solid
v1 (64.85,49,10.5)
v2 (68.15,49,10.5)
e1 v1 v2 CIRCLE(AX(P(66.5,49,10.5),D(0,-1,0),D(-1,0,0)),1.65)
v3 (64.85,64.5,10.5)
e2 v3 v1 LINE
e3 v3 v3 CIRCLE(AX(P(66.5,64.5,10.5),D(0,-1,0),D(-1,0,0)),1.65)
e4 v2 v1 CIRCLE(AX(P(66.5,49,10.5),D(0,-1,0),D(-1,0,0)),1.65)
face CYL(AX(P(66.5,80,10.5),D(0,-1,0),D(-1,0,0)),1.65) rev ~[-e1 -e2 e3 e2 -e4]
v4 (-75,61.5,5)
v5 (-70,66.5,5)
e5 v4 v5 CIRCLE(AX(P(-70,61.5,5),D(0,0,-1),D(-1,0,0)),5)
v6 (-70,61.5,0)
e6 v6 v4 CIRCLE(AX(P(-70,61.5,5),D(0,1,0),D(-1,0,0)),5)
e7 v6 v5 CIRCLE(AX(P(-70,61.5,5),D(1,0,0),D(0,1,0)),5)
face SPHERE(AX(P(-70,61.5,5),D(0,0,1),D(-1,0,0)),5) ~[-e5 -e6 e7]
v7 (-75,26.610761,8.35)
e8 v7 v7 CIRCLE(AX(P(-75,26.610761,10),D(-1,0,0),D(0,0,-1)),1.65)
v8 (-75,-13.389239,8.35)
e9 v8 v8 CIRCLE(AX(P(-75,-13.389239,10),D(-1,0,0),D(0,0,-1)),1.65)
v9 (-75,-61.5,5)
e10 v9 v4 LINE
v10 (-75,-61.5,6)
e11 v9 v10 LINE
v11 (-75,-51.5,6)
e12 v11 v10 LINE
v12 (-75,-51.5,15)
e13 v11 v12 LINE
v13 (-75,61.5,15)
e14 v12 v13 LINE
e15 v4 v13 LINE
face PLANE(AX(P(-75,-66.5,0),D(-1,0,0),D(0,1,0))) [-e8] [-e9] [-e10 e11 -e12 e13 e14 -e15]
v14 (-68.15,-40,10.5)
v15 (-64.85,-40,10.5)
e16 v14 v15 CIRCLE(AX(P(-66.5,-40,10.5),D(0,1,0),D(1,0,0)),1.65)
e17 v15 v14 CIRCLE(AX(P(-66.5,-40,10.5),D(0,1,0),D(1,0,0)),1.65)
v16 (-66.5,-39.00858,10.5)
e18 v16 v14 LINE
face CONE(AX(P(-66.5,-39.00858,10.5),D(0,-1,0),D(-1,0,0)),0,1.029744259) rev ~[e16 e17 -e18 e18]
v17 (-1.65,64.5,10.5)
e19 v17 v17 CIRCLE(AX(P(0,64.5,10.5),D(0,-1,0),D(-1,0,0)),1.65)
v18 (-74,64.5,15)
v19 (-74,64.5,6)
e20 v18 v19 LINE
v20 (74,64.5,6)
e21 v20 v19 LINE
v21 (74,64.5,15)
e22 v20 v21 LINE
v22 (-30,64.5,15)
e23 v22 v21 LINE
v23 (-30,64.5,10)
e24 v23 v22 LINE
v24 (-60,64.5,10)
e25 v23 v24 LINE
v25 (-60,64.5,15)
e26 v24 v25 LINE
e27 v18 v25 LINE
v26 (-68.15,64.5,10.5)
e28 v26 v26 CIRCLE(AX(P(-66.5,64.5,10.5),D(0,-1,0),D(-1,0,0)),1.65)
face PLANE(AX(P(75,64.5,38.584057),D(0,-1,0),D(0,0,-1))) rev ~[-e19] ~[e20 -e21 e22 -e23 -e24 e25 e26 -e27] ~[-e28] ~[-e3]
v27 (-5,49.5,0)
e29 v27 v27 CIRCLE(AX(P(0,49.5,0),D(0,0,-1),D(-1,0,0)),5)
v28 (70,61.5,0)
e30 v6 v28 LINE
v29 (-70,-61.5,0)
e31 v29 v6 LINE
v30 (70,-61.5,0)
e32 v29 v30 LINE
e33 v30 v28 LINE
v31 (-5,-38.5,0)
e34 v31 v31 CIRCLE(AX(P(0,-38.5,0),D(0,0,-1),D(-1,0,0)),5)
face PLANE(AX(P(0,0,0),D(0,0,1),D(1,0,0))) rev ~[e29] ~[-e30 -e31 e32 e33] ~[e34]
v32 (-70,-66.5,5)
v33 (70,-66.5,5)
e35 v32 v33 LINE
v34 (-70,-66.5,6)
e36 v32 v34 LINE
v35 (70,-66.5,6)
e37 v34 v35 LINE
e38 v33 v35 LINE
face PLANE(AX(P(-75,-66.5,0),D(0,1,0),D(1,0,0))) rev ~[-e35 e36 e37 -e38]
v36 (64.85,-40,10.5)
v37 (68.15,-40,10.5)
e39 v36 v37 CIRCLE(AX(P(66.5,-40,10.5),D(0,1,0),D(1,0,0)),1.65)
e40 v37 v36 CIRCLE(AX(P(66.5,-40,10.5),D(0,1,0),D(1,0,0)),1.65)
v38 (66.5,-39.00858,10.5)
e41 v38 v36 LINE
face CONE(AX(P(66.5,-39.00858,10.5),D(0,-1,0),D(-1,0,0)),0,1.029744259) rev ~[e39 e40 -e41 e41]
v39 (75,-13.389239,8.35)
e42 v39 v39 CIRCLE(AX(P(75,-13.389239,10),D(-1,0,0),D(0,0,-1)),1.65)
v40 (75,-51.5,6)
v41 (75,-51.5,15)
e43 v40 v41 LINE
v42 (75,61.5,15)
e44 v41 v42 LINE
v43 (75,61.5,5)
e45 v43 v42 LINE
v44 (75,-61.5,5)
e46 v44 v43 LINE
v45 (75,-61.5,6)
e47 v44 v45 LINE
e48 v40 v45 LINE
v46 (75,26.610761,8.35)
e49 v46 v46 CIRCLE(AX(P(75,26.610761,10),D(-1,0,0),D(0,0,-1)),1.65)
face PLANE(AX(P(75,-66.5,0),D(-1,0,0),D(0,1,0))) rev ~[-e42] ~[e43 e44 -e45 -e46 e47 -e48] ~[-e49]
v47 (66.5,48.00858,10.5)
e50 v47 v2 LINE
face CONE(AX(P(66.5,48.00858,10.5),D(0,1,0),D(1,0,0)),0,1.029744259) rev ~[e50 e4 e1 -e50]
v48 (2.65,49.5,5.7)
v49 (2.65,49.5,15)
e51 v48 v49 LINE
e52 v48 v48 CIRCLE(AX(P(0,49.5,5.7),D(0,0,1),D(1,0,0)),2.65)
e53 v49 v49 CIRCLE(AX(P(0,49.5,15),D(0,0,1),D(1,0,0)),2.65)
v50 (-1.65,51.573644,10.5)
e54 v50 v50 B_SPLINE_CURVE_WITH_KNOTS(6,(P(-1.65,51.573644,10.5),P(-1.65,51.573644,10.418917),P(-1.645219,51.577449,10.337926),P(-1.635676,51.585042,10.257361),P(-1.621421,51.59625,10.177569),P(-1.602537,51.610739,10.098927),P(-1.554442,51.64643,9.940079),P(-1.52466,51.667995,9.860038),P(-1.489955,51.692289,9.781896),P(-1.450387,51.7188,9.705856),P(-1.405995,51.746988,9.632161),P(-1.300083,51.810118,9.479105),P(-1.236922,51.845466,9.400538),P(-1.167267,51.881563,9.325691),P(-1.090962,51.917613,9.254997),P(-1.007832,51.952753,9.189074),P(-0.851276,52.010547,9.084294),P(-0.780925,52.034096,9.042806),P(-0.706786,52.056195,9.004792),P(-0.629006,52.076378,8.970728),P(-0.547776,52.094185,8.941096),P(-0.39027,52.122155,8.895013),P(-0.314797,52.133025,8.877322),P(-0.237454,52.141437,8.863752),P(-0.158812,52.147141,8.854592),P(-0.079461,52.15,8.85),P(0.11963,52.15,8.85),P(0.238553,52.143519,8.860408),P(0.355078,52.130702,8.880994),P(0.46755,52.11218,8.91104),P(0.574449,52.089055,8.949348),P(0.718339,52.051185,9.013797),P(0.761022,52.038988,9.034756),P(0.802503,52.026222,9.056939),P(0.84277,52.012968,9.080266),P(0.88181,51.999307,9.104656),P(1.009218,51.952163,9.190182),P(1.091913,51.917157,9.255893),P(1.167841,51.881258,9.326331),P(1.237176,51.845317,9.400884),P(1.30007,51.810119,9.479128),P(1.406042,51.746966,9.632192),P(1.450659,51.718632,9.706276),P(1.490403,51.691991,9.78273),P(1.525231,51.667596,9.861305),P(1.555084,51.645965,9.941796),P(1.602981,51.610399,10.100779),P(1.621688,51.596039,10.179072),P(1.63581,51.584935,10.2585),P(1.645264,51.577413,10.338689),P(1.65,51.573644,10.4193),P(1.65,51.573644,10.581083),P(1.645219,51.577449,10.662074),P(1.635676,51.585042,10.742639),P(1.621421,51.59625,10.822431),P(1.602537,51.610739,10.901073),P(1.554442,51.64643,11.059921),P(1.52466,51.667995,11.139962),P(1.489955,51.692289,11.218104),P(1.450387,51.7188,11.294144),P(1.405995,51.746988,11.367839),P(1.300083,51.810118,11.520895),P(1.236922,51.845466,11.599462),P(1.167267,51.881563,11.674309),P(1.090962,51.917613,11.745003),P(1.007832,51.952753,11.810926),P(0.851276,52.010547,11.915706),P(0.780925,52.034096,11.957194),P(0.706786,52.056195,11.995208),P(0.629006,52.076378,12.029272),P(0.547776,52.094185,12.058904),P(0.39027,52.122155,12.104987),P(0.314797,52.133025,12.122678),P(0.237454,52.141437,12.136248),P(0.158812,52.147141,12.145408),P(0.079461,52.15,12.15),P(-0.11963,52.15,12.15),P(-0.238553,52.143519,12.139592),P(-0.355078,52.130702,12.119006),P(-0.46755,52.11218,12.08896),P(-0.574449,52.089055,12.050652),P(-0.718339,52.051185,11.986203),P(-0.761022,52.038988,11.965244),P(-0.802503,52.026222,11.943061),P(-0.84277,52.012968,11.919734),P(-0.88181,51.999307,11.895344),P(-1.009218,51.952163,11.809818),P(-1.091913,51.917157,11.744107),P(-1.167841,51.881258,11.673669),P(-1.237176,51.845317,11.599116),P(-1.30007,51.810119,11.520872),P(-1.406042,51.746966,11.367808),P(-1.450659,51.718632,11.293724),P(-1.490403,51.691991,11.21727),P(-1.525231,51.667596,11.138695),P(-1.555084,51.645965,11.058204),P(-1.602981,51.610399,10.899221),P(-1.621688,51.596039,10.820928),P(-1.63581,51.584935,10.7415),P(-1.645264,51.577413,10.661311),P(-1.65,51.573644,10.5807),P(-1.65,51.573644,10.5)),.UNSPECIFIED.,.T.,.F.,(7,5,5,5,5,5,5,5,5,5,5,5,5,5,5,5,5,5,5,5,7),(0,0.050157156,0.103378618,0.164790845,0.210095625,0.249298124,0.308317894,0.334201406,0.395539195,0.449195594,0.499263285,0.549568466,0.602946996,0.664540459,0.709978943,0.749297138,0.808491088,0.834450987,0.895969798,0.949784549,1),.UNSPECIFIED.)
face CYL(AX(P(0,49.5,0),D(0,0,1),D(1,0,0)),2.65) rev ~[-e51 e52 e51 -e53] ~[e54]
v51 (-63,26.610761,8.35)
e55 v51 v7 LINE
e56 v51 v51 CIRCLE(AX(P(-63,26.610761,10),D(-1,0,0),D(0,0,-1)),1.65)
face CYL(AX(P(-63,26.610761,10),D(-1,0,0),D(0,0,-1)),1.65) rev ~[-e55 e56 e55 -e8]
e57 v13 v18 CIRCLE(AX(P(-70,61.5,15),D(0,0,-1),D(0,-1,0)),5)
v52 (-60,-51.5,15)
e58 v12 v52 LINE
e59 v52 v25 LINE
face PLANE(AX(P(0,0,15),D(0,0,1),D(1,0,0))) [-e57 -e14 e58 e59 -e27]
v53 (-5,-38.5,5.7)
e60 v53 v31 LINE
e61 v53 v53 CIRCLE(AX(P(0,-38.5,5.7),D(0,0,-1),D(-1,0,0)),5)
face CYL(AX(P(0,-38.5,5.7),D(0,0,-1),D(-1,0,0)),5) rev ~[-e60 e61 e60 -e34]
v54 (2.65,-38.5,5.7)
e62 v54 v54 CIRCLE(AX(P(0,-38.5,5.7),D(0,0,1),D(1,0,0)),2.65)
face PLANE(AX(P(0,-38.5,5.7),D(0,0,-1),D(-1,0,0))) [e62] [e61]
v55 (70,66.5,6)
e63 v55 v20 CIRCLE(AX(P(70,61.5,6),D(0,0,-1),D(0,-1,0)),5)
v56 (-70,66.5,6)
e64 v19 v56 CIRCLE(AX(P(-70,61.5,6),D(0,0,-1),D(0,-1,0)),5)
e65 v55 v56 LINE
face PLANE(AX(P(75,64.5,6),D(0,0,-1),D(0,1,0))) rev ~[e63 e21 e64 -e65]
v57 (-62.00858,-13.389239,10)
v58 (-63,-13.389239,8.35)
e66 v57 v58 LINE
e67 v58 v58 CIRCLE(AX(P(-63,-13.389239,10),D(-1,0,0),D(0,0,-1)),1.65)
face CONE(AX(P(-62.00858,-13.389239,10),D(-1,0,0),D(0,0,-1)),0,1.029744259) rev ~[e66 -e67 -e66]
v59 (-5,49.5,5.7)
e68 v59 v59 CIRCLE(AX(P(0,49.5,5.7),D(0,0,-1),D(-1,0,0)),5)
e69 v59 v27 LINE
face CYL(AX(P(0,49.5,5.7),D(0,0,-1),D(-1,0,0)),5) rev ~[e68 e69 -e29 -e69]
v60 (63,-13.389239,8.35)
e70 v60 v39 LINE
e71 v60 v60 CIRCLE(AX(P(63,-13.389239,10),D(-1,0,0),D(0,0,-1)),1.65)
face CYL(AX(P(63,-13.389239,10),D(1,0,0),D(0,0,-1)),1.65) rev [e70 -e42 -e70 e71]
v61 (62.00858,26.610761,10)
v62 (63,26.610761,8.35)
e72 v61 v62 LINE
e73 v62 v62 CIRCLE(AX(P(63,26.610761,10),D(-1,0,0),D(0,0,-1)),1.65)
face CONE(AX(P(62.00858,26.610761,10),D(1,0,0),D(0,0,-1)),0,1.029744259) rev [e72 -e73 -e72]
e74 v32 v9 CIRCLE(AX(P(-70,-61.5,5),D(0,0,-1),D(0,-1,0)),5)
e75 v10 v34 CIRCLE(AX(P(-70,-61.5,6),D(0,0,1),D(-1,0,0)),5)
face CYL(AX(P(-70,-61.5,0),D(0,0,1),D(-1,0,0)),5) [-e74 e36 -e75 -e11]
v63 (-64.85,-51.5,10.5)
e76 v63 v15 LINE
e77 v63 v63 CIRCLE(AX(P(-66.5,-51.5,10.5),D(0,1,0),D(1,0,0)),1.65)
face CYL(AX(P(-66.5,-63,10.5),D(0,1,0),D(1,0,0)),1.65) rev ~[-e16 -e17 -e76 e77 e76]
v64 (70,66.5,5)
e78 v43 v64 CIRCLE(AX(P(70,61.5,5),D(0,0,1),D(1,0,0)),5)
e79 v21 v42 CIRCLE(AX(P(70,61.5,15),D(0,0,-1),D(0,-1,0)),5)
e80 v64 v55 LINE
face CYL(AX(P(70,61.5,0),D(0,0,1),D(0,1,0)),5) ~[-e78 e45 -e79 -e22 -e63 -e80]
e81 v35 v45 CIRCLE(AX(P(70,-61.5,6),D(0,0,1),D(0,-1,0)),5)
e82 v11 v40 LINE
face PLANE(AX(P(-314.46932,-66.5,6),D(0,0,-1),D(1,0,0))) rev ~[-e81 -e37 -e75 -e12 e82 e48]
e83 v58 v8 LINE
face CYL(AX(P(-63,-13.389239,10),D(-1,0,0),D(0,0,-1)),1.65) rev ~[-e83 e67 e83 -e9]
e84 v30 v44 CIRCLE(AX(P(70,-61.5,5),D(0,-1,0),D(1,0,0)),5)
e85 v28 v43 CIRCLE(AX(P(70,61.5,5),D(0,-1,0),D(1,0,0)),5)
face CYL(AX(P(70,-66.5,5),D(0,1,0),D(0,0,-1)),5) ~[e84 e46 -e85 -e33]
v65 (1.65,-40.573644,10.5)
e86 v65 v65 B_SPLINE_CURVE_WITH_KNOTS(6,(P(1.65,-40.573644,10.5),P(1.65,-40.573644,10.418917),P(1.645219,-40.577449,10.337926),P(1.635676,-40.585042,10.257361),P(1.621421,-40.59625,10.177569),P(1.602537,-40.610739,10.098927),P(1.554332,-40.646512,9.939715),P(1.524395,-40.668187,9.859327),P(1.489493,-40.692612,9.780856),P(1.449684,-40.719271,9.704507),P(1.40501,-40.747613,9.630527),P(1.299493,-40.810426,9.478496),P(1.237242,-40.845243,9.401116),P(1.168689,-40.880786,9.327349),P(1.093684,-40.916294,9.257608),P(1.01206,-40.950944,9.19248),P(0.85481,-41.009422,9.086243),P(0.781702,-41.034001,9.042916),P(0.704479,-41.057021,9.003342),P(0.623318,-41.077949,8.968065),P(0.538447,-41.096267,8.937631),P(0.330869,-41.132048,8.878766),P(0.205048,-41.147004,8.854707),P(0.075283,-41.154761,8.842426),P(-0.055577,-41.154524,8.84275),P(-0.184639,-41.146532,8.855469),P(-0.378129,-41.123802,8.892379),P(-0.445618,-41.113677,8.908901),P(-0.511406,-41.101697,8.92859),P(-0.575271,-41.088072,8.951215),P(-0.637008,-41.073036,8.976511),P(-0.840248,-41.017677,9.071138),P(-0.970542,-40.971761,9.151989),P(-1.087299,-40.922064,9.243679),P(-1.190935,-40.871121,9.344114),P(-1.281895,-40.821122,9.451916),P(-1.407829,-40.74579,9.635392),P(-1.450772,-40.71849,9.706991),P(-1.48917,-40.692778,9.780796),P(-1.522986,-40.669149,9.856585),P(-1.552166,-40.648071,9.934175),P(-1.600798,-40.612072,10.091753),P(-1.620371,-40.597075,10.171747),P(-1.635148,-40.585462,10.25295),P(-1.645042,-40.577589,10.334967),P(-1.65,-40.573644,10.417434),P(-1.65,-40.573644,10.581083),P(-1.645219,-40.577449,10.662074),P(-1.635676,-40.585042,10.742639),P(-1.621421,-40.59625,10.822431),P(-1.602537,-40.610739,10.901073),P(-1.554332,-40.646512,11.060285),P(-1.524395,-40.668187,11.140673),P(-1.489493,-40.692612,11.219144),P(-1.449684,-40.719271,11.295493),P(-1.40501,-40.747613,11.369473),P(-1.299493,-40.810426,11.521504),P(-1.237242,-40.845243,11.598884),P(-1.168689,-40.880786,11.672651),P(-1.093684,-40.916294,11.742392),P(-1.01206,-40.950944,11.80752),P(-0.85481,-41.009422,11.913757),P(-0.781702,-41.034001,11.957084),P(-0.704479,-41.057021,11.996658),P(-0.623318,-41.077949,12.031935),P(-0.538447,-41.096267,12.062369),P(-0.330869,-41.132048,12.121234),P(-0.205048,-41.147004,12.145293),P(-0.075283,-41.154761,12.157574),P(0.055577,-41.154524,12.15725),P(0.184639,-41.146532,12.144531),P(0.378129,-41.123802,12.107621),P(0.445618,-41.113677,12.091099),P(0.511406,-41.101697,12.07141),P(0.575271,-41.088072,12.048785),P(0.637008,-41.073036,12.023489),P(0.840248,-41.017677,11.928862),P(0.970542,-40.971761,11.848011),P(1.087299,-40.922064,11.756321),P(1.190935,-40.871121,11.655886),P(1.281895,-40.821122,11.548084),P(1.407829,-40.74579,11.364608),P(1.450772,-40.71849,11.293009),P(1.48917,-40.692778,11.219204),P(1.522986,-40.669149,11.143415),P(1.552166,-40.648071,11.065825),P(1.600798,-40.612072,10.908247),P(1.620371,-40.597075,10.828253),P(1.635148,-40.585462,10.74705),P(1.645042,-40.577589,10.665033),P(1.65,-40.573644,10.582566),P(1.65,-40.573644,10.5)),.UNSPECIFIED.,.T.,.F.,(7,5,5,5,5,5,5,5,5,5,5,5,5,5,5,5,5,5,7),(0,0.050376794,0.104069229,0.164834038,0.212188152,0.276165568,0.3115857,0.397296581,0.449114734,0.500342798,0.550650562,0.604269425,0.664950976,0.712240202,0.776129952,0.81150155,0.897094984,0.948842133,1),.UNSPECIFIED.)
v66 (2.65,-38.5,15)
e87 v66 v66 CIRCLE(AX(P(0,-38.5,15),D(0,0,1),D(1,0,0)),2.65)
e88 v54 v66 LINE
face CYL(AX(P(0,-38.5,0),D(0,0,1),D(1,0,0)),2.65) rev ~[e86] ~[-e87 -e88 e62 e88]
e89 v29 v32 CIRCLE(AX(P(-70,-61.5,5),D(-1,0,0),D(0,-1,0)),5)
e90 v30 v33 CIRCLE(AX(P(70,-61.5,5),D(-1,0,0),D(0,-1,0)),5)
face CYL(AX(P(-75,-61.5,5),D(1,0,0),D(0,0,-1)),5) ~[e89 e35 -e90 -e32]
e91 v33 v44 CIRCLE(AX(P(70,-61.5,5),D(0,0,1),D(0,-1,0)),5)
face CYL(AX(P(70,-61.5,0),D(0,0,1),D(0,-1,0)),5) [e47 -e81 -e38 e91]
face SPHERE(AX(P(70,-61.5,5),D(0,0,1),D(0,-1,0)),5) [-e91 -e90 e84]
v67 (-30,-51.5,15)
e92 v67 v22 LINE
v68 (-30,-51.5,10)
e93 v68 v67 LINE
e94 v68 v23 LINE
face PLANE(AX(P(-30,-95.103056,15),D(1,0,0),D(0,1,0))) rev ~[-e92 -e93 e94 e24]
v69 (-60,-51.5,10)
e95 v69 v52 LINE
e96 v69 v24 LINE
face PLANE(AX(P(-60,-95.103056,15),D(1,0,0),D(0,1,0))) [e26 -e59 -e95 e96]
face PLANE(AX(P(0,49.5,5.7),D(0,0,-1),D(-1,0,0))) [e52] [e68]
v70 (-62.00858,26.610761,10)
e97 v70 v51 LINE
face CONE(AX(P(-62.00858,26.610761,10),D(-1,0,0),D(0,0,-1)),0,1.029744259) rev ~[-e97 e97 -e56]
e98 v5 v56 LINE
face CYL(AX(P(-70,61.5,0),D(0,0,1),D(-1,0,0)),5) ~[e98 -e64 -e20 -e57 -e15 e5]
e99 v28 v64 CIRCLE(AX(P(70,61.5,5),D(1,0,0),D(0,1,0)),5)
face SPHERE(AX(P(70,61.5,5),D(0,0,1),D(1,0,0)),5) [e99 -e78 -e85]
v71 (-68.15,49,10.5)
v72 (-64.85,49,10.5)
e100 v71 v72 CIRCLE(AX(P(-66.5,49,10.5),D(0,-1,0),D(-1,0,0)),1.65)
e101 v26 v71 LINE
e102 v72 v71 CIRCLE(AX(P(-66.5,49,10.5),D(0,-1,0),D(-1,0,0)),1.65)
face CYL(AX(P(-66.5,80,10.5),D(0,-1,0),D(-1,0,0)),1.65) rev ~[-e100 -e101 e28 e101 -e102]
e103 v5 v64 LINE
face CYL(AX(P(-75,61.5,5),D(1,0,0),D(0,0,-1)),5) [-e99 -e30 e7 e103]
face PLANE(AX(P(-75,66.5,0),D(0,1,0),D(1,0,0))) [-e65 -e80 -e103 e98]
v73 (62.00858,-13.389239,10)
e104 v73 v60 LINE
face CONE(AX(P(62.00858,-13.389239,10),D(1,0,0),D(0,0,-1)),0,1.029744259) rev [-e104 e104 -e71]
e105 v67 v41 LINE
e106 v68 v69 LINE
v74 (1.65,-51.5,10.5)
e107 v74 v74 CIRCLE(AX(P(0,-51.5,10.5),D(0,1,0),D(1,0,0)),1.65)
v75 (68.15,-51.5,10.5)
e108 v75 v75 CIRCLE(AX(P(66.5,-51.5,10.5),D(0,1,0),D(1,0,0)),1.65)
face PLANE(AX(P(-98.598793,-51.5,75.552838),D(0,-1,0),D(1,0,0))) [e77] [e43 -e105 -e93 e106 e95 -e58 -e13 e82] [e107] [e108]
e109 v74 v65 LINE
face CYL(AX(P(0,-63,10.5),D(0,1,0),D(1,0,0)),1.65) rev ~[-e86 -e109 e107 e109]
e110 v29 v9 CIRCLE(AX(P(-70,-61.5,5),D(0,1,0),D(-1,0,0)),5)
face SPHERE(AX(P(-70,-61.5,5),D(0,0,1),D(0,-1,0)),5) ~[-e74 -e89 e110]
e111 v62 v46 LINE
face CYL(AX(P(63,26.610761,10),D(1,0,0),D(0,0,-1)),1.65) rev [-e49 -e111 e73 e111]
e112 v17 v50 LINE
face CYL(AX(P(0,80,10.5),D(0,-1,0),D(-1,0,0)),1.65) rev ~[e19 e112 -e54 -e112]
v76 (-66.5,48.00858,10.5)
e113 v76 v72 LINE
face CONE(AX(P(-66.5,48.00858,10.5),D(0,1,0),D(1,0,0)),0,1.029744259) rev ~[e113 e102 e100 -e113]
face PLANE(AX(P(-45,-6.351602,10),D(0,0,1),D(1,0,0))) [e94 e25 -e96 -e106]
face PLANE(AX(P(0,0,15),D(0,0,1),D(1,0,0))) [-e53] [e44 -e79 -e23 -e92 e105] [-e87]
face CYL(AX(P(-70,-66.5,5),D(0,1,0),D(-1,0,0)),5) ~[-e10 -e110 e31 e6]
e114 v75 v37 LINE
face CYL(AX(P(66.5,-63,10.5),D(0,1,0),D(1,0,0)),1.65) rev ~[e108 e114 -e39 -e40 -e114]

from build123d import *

# Parameters (mm, degrees)
SKETCH_1_W                  = 150
SKETCH_1_H                  = 133
EXTRUDE_1_DEPTH             = 15
SKETCH_2_W                  = 32.584056601
SKETCH_2_H                  = 28.363937547
CUT_EXTRUDE_1_DEPTH         = 165.764225486
FILLET_8_R                  = 5
HOLE_WIZARD_1_D             = 5.3
HOLE_WIZARD_1_CBORE_D       = 10
HOLE_WIZARD_1_CBORE_DEPTH   = 5.7
HOLE_WIZARD_M4_3_D          = 3.3
HOLE_WIZARD_M4_3_DEPTH      = 15.5
HOLE_WIZARD_M4_3_TIP        = 0.991420021
SKETCH_20_W                 = 431.741055117
SKETCH_20_H                 = 139.105675049
CUT_EXTRUDE_5_DEPTH         = 15
SKETCH_24_W                 = 30
SKETCH_24_H                 = 177.502907688
CUT_EXTRUDE_6_DEPTH         = 5
HOLE_WIZARD_M4_2_D          = 3.3
HOLE_WIZARD_M4_2_DEPTH      = 11.5
HOLE_WIZARD_M4_2_TIP        = 0.991420021
HOLE_WIZARD_M4_1_AT_2_COUNT = 2
HOLE_WIZARD_M4_1_AT_2_PITCH = 40


with BuildPart() as part:
    # 草图1 → 凸台-拉伸1 (new body)
    with BuildSketch(Plane.XY):
        Rectangle(SKETCH_1_W, SKETCH_1_H)
    extrude(amount=EXTRUDE_1_DEPTH)

    # 草图2 → 切除-拉伸1 (cut, through all)
    with BuildSketch(Plane(origin=(75, 0, 0), x_dir=(0, 0, -1), z_dir=(1, 0, 0))):
        with Locations((-22.292028301, 78.681968774)):
            Rectangle(SKETCH_2_W, SKETCH_2_H)
    extrude(amount=-CUT_EXTRUDE_1_DEPTH, mode=Mode.SUBTRACT)

    # 圆角8
    fillet_8_edges = [part.edges().sort_by_distance(p)[0] for p in [
        (75, 66.5, 3),
        (-75, 66.5, 3),
        (-75, -66.5, 7.5),
        (75, -66.5, 7.5),
        (0, -66.5, 0),
        (-75, 0, 0),
        (75, 0, 0),
        (0, 66.5, 0),
    ]]
    fillet(fillet_8_edges, radius=FILLET_8_R)

    # 打孔尺寸(%根据)开槽圆柱头螺钉的类型1 (through all)
    with Locations(Plane(origin=(0, 0, 0), x_dir=(-1, 0, 0), z_dir=(0, 0, -1))):
        with Locations((0, 49.5), (0, -38.5)):
            CounterBoreHole(HOLE_WIZARD_1_D / 2, HOLE_WIZARD_1_CBORE_D / 2, HOLE_WIZARD_1_CBORE_DEPTH)

    # M4 螺纹孔3
    with Locations(Plane(origin=(0, 64.5, 0), x_dir=(1, 0, 0), z_dir=(0, 1, 0))):
        with Locations((0, -10.5), (66.5, -10.5), (-66.5, -10.5)):
            Hole(HOLE_WIZARD_M4_3_D / 2, depth=HOLE_WIZARD_M4_3_DEPTH)
            with Locations((0, 0, -(HOLE_WIZARD_M4_3_DEPTH + HOLE_WIZARD_M4_3_TIP / 2))):  # 118° drill point
                Cone(0, HOLE_WIZARD_M4_3_D / 2, HOLE_WIZARD_M4_3_TIP, mode=Mode.SUBTRACT)

    # 草图20 → 切除-拉伸5 (cut)
    with BuildSketch(Plane.XZ.offset(66.5)):
        with Locations((-98.598792732, 75.552837525)):
            Rectangle(SKETCH_20_W, SKETCH_20_H)
    extrude(amount=-CUT_EXTRUDE_5_DEPTH, mode=Mode.SUBTRACT)

    # 草图24 → 切除-拉伸6 (cut)
    with BuildSketch(Plane.XY.offset(15)):
        with Locations((-45, -6.351602415)):
            Rectangle(SKETCH_24_W, SKETCH_24_H)
    extrude(amount=-CUT_EXTRUDE_6_DEPTH, mode=Mode.SUBTRACT)

    # M4 螺纹孔2
    with Locations(Plane(origin=(0, -51.5, 0), x_dir=(-1, 0, 0), z_dir=(0, -1, 0))):
        with Locations((66.5, -10.5), (0, -10.5), (-66.5, -10.5)):
            Hole(HOLE_WIZARD_M4_2_D / 2, depth=HOLE_WIZARD_M4_2_DEPTH)
            with Locations((0, 0, -(HOLE_WIZARD_M4_2_DEPTH + HOLE_WIZARD_M4_2_TIP / 2))):  # 118° drill point
                Cone(0, HOLE_WIZARD_M4_2_D / 2, HOLE_WIZARD_M4_2_TIP, mode=Mode.SUBTRACT)

    # 草图28 → M4 螺纹孔1 (revolve, cut)
    with BuildSketch(Plane(origin=(75, 26.61076125, 10), x_dir=(0, 0, -1), z_dir=(0, 1, 0))):
        Polygon((0, 0), (0, 12.991420021), (1.65, 12), (1.65, 0), align=None)
    hole_wizard_m4_1 = revolve(axis=Axis((81.35, 26.61076125, 10), (-1, 0, 0)), mode=Mode.SUBTRACT)

    # M4 螺纹孔1 at 2: M4 螺纹孔1 ×2
    with Locations(*[(0, -i * HOLE_WIZARD_M4_1_AT_2_PITCH, 0) for i in range(1, HOLE_WIZARD_M4_1_AT_2_COUNT)]):
        add(hole_wizard_m4_1, mode=Mode.SUBTRACT)

    # 镜向1: M4 螺纹孔1 across plane
    add(hole_wizard_m4_1.mirror(Plane(origin=(0, 0, 0), x_dir=(0, 0, 1), z_dir=(1, 0, 0))), mode=Mode.SUBTRACT)

    # 镜向1 copy 1 sketch → 镜向1 copy 1 (revolve, cut)
    with BuildSketch(Plane(origin=(-75, -13.38923875, 10), x_dir=(0, 0, -1), z_dir=(0, 1, 0))):
        Polygon((0, 0), (0, -12.991420021), (1.65, -12), (1.65, 0), align=None)
    revolve(axis=Axis((-81.35, -13.38923875, 10), (-1, 0, 0)), mode=Mode.SUBTRACT)


solid = part.part
